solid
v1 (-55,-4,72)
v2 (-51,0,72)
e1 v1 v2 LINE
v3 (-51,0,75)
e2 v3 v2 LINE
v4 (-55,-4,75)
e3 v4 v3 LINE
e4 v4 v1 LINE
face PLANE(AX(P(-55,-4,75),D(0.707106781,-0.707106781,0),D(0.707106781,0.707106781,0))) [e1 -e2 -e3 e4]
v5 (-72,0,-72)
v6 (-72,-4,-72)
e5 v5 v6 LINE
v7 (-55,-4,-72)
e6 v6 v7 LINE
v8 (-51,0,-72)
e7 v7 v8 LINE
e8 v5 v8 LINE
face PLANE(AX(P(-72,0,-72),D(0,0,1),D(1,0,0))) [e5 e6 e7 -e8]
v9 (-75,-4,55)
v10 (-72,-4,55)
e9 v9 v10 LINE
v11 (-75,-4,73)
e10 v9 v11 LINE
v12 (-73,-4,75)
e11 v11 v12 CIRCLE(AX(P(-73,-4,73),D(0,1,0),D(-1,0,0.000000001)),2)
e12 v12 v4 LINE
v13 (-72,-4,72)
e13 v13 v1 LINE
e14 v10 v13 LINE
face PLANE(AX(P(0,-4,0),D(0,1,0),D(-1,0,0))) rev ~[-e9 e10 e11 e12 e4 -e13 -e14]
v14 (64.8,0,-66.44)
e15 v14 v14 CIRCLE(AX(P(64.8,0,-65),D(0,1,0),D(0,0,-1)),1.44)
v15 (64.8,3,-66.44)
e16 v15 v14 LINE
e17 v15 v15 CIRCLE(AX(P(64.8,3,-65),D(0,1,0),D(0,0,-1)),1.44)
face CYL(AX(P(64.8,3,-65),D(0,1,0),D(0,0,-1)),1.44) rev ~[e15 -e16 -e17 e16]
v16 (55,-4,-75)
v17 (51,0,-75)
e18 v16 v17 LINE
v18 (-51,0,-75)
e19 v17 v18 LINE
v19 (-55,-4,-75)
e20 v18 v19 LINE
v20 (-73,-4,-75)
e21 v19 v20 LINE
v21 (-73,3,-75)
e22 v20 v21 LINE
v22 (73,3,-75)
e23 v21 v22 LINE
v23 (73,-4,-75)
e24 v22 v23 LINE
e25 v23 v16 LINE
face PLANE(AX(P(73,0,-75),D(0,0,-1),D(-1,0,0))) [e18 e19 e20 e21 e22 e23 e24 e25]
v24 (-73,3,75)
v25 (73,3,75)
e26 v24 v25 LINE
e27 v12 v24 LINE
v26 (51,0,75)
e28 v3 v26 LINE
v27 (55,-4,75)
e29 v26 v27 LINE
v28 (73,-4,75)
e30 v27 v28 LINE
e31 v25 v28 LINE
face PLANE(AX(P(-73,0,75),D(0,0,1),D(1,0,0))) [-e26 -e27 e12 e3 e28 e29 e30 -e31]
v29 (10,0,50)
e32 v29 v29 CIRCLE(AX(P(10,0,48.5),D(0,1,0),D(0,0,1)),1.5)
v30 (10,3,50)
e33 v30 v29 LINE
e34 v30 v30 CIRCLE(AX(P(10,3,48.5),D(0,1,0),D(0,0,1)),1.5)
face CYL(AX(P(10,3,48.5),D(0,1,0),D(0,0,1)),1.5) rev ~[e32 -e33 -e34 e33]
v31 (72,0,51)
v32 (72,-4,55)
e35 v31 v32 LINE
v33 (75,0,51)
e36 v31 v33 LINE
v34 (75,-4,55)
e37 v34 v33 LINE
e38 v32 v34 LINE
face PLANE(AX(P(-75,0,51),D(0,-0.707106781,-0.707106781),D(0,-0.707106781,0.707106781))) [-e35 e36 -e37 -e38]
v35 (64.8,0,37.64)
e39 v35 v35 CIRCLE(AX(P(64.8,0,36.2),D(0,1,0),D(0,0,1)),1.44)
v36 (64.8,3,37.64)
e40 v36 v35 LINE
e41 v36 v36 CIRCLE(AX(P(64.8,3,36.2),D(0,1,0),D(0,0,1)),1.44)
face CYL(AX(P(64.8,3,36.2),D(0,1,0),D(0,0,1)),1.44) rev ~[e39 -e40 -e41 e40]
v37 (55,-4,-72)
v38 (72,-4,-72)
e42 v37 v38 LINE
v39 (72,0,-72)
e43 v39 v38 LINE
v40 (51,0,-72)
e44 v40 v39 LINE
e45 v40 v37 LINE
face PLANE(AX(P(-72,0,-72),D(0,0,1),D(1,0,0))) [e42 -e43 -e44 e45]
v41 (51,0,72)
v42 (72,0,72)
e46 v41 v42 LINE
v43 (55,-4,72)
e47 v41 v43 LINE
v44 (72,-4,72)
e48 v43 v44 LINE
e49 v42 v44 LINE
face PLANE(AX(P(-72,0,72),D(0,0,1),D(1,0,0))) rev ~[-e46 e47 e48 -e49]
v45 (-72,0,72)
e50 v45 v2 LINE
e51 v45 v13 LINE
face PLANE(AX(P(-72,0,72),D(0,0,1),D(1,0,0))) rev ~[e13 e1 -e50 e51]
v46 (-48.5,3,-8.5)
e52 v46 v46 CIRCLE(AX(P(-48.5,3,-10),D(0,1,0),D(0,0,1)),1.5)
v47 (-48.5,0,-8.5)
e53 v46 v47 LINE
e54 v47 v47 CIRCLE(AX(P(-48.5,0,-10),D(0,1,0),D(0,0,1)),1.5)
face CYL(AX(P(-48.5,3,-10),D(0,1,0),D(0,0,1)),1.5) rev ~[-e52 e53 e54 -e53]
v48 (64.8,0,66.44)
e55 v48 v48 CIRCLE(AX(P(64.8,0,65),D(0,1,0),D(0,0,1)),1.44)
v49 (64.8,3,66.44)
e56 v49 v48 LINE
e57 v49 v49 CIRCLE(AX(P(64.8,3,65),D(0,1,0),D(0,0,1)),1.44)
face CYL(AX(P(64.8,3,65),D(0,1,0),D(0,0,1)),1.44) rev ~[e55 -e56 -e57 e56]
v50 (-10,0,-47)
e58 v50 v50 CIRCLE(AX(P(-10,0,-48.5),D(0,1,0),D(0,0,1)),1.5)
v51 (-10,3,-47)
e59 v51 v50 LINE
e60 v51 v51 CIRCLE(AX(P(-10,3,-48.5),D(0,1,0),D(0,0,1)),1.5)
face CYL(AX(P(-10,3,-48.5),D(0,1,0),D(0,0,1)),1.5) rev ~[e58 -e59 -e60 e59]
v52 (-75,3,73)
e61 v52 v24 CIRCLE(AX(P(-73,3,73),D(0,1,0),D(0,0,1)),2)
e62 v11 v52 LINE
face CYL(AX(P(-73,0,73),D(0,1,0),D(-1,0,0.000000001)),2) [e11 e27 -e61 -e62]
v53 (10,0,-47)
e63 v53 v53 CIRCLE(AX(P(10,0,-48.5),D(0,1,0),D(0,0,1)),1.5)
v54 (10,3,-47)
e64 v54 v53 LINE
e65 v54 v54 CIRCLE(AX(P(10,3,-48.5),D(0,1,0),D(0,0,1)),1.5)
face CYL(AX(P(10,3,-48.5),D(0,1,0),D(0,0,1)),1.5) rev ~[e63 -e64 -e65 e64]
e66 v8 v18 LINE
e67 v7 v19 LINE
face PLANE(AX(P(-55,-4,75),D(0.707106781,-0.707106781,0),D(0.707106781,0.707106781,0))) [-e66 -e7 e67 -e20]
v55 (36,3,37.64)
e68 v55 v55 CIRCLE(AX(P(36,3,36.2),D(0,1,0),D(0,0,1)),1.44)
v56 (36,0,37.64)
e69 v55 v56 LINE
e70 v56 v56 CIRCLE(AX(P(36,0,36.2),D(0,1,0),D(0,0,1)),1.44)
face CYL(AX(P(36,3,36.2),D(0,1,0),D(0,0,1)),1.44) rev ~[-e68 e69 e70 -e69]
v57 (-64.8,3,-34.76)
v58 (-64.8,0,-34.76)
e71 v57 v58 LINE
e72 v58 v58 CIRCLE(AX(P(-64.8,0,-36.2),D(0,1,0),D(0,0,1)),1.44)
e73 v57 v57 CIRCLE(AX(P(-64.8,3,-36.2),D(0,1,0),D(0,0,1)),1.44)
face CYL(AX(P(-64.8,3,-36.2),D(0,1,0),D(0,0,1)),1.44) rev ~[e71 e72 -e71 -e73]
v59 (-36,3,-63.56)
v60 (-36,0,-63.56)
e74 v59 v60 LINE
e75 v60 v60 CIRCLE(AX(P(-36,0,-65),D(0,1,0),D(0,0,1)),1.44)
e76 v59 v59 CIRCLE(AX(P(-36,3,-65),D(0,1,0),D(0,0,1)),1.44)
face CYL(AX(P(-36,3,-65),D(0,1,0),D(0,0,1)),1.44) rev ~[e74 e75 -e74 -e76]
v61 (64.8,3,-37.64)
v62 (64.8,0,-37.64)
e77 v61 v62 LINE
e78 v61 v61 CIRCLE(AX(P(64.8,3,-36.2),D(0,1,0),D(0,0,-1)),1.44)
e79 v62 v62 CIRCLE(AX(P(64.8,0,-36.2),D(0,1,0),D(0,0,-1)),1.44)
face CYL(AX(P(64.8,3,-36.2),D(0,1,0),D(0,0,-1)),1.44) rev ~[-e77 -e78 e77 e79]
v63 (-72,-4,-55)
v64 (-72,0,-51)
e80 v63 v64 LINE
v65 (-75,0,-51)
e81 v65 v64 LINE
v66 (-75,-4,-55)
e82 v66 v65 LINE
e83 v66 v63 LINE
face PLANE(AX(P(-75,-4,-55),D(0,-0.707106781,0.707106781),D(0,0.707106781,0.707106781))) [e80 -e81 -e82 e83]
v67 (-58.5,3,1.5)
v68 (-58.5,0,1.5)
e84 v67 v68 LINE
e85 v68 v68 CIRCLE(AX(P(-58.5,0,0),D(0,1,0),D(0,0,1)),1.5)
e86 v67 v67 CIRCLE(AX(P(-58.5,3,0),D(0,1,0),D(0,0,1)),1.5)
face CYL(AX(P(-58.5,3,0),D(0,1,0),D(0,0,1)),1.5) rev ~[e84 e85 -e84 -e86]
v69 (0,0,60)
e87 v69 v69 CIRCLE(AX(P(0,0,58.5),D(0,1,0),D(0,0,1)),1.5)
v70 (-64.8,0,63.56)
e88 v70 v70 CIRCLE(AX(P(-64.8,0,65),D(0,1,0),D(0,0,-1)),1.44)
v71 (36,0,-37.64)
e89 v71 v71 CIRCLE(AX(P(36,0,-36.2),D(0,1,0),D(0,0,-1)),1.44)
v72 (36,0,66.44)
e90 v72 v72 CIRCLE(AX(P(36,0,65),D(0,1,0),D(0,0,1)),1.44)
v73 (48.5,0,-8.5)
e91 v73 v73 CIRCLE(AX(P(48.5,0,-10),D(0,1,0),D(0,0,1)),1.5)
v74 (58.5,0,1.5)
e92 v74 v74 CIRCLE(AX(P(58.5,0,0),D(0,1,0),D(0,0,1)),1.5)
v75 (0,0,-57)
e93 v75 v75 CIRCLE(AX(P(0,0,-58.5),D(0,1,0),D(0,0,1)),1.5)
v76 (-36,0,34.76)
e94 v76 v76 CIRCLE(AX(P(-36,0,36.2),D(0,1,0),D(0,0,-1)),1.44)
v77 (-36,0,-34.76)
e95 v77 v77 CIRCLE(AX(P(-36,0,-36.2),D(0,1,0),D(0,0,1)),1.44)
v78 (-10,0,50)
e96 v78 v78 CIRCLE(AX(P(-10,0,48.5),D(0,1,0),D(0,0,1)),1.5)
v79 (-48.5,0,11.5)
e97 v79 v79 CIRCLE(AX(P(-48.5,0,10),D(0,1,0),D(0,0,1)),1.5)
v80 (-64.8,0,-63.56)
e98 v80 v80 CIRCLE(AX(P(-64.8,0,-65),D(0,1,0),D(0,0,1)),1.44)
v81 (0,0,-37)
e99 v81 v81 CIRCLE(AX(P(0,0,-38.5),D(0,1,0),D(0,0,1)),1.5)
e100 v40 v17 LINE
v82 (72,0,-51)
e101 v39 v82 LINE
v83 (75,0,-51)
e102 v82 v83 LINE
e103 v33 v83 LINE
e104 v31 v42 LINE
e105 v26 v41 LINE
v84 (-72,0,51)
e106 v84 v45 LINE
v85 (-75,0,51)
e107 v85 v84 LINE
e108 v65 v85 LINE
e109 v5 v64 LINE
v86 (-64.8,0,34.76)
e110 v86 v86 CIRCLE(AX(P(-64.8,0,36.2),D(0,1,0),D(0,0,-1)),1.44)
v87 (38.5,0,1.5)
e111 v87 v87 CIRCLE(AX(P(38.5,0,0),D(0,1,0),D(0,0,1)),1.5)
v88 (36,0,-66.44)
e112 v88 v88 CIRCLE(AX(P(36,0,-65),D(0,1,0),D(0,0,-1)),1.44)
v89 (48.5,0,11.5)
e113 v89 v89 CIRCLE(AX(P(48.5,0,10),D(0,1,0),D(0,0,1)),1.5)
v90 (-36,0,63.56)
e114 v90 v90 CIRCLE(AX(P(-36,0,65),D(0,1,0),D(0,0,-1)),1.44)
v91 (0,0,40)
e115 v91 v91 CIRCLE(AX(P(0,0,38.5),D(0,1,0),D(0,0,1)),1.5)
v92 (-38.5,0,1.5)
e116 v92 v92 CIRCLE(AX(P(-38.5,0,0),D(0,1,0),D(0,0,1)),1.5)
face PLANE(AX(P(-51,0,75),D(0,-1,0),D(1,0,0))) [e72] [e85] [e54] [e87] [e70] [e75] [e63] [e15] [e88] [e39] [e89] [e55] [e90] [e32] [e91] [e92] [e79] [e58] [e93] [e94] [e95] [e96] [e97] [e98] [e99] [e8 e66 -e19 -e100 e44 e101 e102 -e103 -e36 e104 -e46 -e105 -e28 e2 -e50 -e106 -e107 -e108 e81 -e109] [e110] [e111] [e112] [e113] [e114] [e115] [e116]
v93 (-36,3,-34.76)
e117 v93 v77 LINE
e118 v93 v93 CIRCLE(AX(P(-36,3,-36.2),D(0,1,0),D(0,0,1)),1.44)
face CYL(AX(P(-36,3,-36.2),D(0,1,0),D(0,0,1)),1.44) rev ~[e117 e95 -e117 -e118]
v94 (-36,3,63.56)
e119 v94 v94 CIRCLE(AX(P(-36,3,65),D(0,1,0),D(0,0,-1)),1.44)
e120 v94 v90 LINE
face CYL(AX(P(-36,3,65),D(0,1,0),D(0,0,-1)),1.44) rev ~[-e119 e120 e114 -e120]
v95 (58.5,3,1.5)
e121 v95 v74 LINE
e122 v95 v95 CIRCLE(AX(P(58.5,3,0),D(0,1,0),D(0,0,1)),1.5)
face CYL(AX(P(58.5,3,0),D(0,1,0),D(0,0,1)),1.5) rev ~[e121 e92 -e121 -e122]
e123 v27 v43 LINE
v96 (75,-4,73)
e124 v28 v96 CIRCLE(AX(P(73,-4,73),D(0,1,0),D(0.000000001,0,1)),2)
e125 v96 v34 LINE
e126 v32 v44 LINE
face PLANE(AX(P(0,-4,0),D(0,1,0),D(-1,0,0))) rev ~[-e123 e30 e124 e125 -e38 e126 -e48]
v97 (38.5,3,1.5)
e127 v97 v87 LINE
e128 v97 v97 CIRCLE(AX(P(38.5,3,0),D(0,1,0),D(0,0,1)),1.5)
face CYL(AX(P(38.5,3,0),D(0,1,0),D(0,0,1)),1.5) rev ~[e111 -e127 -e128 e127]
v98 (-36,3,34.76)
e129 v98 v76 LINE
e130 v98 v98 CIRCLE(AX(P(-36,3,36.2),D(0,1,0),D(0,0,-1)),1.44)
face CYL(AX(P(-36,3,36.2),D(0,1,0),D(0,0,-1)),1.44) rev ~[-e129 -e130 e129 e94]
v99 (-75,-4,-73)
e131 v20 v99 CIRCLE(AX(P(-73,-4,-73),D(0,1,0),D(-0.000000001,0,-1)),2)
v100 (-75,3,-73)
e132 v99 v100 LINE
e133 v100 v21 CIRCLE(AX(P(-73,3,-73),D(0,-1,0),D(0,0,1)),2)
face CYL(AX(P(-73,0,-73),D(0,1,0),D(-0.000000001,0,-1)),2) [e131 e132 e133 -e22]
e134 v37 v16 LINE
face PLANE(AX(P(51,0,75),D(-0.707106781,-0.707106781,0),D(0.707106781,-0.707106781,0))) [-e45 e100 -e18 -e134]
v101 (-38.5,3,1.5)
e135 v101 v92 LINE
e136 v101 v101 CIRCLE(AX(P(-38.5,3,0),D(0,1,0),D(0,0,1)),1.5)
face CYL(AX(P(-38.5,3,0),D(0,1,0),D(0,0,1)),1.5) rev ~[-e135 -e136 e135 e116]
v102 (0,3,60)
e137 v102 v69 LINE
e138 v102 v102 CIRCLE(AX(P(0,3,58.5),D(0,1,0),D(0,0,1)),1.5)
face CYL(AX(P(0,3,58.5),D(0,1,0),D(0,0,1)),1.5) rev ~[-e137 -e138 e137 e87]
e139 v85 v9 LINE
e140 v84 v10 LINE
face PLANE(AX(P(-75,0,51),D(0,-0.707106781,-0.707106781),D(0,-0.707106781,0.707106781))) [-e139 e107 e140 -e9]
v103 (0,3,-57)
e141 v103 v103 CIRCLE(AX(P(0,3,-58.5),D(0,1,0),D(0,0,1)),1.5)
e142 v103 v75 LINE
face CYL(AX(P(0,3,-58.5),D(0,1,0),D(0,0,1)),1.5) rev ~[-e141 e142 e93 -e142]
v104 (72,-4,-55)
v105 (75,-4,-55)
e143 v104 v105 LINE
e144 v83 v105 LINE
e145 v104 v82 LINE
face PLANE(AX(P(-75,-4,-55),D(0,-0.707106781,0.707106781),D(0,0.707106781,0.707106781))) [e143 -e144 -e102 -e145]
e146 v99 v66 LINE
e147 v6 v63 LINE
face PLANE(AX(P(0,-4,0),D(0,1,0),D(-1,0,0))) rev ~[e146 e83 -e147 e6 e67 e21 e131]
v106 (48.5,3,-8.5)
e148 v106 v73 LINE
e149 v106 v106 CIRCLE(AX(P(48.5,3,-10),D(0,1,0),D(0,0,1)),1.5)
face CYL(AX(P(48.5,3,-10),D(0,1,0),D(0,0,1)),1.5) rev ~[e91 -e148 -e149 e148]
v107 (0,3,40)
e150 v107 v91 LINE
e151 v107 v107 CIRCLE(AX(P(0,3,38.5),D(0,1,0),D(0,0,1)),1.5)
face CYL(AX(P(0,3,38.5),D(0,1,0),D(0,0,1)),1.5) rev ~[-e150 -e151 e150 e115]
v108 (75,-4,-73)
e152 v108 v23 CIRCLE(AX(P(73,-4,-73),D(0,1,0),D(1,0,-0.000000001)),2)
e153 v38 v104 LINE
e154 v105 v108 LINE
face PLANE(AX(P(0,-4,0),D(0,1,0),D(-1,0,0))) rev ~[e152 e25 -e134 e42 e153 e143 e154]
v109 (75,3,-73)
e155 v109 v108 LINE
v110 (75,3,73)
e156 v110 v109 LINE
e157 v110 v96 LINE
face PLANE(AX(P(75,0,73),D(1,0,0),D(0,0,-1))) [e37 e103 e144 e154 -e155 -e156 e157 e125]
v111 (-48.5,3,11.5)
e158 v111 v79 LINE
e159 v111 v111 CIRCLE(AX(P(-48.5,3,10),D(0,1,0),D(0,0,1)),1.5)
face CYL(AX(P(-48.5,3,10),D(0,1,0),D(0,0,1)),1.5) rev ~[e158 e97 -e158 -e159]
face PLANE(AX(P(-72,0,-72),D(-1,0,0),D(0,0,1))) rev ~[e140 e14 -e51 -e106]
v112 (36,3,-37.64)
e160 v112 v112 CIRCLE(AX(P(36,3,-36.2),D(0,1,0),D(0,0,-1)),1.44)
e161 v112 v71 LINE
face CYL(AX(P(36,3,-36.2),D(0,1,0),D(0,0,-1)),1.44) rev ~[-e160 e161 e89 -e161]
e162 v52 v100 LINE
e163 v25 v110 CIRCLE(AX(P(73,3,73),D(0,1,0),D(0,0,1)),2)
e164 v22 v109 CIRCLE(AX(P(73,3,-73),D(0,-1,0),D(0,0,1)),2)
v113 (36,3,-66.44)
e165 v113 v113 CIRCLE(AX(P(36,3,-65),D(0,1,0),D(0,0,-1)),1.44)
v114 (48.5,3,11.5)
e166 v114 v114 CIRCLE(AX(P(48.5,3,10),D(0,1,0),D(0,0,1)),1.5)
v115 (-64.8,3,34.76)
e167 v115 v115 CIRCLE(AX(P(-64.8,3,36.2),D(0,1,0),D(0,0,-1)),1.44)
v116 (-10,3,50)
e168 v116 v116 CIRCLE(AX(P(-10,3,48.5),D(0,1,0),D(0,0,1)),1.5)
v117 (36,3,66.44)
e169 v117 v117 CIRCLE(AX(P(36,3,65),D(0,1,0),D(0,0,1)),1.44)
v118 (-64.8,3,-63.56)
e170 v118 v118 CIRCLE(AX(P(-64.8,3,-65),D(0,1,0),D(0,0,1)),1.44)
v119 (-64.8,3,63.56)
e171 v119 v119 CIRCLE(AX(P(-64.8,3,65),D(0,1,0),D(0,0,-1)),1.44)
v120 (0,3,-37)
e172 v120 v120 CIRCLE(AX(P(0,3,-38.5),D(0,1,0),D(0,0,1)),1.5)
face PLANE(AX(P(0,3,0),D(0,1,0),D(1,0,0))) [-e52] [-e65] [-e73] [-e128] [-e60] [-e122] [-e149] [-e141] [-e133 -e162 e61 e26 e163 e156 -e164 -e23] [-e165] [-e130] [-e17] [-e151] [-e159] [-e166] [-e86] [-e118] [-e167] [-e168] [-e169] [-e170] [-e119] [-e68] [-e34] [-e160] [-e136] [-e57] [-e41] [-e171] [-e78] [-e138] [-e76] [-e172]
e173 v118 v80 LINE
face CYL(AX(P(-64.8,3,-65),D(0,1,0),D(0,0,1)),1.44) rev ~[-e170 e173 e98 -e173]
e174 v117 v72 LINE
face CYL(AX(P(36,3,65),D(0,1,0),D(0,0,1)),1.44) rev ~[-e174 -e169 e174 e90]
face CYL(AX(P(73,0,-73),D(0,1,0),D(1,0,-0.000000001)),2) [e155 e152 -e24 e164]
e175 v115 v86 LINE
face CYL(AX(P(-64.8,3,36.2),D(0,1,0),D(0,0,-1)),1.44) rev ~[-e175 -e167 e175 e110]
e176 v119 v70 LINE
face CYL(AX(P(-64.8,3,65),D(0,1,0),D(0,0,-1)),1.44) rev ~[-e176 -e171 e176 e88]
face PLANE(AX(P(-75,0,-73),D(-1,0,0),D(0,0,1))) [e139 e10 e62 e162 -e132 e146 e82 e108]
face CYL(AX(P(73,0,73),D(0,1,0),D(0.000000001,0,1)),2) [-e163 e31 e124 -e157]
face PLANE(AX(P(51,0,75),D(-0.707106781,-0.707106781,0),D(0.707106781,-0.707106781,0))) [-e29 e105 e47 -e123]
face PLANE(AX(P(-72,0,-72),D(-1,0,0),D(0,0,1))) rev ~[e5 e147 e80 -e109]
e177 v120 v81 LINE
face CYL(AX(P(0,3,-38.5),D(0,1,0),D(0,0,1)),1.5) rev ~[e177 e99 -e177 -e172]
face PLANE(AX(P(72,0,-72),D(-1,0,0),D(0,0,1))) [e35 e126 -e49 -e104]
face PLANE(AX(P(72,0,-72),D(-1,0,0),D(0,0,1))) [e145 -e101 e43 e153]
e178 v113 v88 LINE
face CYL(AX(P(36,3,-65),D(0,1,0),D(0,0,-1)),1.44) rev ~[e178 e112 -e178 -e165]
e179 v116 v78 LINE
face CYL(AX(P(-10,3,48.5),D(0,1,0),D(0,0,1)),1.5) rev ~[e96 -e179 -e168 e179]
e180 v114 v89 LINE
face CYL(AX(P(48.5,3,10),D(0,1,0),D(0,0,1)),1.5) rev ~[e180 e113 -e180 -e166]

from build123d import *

# Parameters (mm, degrees)
SKETCH1_W           = 150
SKETCH1_H           = 150
BOSS_EXTRUDE1_DEPTH = 3
SKETCH2_R           = 1.44
CUT_EXTRUDE1_DEPTH  = 107.108435103
SKETCH3_R           = 1.5
CUT_EXTRUDE2_DEPTH  = 107.108435103
FILLET1_R           = 2
SKETCH4_W           = 144
SKETCH4_H           = 144
BOSS_EXTRUDE2_DEPTH = 4
CUT_EXTRUDE3_DEPTH  = 168.752794314
CUT_EXTRUDE4_DEPTH  = 168.752794314


with BuildPart() as part:
    # Sketch1 → Boss-Extrude1 (new body)
    with BuildSketch(Plane(origin=(0, 0, 0), x_dir=(1, 0, 0), z_dir=(0, 1, 0))):
        Rectangle(SKETCH1_W, SKETCH1_H)
    extrude(amount=BOSS_EXTRUDE1_DEPTH)

    # Sketch2 → Cut-Extrude1 (cut, through all)
    with BuildSketch(Plane(origin=(0, 3, 0), x_dir=(1, 0, 0), z_dir=(0, 1, 0))):
        with Locations(Location((-64.8, 65, 0), (0, 0, 270))):
            Circle(SKETCH2_R)
        with Locations(Location((-36, 65, 0), (0, 0, 270))):
            Circle(SKETCH2_R)
        with Locations(Location((-64.8, 36.2, 0), (0, 0, 270))):
            Circle(SKETCH2_R)
        with Locations(Location((-36, 36.2, 0), (0, 0, 270))):
            Circle(SKETCH2_R)
        with Locations(Location((36, 65, 0), (0, 0, 90))):
            Circle(SKETCH2_R)
        with Locations(Location((64.8, 65, 0), (0, 0, 90))):
            Circle(SKETCH2_R)
        with Locations(Location((64.8, 36.2, 0), (0, 0, 90))):
            Circle(SKETCH2_R)
        with Locations(Location((36, 36.2, 0), (0, 0, 90))):
            Circle(SKETCH2_R)
        with Locations(Location((-64.8, -36.2, 0), (0, 0, 90))):
            Circle(SKETCH2_R)
        with Locations(Location((-64.8, -65, 0), (0, 0, 90))):
            Circle(SKETCH2_R)
        with Locations(Location((-36, -65, 0), (0, 0, 90))):
            Circle(SKETCH2_R)
        with Locations(Location((-36, -36.2, 0), (0, 0, 90))):
            Circle(SKETCH2_R)
        with Locations(Location((64.8, -65, 0), (0, 0, 270))):
            Circle(SKETCH2_R)
        with Locations(Location((36, -65, 0), (0, 0, 270))):
            Circle(SKETCH2_R)
        with Locations(Location((36, -36.2, 0), (0, 0, 270))):
            Circle(SKETCH2_R)
        with Locations(Location((64.8, -36.2, 0), (0, 0, 270))):
            Circle(SKETCH2_R)
    extrude(amount=-CUT_EXTRUDE1_DEPTH, mode=Mode.SUBTRACT)

    # Sketch3 → Cut-Extrude2 (cut, through all)
    with BuildSketch(Plane(origin=(0, 3, 0), x_dir=(1, 0, 0), z_dir=(0, 1, 0))):
        with Locations(Location((-38.5, 0, 0), (0, 0, 270))):
            Circle(SKETCH3_R)
        with Locations(Location((-48.5, 10, 0), (0, 0, 270))):
            Circle(SKETCH3_R)
        with Locations(Location((-58.5, 0, 0), (0, 0, 270))):
            Circle(SKETCH3_R)
        with Locations(Location((-48.5, -10, 0), (0, 0, 270))):
            Circle(SKETCH3_R)
        with Locations(Location((-10, -48.5, 0), (0, 0, 270))):
            Circle(SKETCH3_R)
        with Locations(Location((0, -58.5, 0), (0, 0, 270))):
            Circle(SKETCH3_R)
        with Locations(Location((10, -48.5, 0), (0, 0, 270))):
            Circle(SKETCH3_R)
        with Locations(Location((0, -38.5, 0), (0, 0, 270))):
            Circle(SKETCH3_R)
        with Locations(Location((58.5, 0, 0), (0, 0, 270))):
            Circle(SKETCH3_R)
        with Locations(Location((48.5, 10, 0), (0, 0, 270))):
            Circle(SKETCH3_R)
        with Locations(Location((38.5, 0, 0), (0, 0, 270))):
            Circle(SKETCH3_R)
        with Locations(Location((0, 38.5, 0), (0, 0, 270))):
            Circle(SKETCH3_R)
        with Locations(Location((10, 48.5, 0), (0, 0, 270))):
            Circle(SKETCH3_R)
        with Locations(Location((0, 58.5, 0), (0, 0, 270))):
            Circle(SKETCH3_R)
        with Locations(Location((-10, 48.5, 0), (0, 0, 270))):
            Circle(SKETCH3_R)
        with Locations(Location((48.5, -10, 0), (0, 0, 270))):
            Circle(SKETCH3_R)
    extrude(amount=-CUT_EXTRUDE2_DEPTH, mode=Mode.SUBTRACT)

    # Fillet1
    fillet1_edges = [part.edges().sort_by_distance(p)[0] for p in [
        (75, 1.5, 75),
        (-75, 1.5, 75),
        (-75, 1.5, -75),
        (75, 1.5, -75),
    ]]
    fillet(fillet1_edges, radius=FILLET1_R)

    # Sketch4 → Boss-Extrude2 (add)
    with BuildSketch(Plane.XZ):
        with BuildLine():
            Line((73, -75), (-73, -75))
            ThreePointArc((-73, -75), (-74.414213562, -74.414213562), (-75, -73))
            Line((-75, -73), (-75, 73))
            ThreePointArc((-75, 73), (-74.414213562, 74.414213562), (-73, 75))
            Line((-73, 75), (73, 75))
            ThreePointArc((73, 75), (74.414213562, 74.414213562), (75, 73))
            Line((75, 73), (75, -73))
            ThreePointArc((75, -73), (74.414213562, -74.414213562), (73, -75))
        make_face()
        Rectangle(SKETCH4_W, SKETCH4_H, mode=Mode.SUBTRACT)
    extrude(amount=BOSS_EXTRUDE2_DEPTH)

    # Sketch5 → Cut-Extrude3 (cut, through all)
    with BuildSketch(Plane.XY.offset(75)):
        Polygon((-55, -4), (-51, 0), (51, 0), (55, -4), align=None)
    extrude(amount=-CUT_EXTRUDE3_DEPTH, mode=Mode.SUBTRACT)

    # Sketch6 → Cut-Extrude4 (cut, through all)
    with BuildSketch(Plane.ZY.offset(75)):
        Polygon((-55, -4), (-51, 0), (51, 0), (55, -4), align=None)
    extrude(amount=-CUT_EXTRUDE4_DEPTH, mode=Mode.SUBTRACT)


solid = part.part
